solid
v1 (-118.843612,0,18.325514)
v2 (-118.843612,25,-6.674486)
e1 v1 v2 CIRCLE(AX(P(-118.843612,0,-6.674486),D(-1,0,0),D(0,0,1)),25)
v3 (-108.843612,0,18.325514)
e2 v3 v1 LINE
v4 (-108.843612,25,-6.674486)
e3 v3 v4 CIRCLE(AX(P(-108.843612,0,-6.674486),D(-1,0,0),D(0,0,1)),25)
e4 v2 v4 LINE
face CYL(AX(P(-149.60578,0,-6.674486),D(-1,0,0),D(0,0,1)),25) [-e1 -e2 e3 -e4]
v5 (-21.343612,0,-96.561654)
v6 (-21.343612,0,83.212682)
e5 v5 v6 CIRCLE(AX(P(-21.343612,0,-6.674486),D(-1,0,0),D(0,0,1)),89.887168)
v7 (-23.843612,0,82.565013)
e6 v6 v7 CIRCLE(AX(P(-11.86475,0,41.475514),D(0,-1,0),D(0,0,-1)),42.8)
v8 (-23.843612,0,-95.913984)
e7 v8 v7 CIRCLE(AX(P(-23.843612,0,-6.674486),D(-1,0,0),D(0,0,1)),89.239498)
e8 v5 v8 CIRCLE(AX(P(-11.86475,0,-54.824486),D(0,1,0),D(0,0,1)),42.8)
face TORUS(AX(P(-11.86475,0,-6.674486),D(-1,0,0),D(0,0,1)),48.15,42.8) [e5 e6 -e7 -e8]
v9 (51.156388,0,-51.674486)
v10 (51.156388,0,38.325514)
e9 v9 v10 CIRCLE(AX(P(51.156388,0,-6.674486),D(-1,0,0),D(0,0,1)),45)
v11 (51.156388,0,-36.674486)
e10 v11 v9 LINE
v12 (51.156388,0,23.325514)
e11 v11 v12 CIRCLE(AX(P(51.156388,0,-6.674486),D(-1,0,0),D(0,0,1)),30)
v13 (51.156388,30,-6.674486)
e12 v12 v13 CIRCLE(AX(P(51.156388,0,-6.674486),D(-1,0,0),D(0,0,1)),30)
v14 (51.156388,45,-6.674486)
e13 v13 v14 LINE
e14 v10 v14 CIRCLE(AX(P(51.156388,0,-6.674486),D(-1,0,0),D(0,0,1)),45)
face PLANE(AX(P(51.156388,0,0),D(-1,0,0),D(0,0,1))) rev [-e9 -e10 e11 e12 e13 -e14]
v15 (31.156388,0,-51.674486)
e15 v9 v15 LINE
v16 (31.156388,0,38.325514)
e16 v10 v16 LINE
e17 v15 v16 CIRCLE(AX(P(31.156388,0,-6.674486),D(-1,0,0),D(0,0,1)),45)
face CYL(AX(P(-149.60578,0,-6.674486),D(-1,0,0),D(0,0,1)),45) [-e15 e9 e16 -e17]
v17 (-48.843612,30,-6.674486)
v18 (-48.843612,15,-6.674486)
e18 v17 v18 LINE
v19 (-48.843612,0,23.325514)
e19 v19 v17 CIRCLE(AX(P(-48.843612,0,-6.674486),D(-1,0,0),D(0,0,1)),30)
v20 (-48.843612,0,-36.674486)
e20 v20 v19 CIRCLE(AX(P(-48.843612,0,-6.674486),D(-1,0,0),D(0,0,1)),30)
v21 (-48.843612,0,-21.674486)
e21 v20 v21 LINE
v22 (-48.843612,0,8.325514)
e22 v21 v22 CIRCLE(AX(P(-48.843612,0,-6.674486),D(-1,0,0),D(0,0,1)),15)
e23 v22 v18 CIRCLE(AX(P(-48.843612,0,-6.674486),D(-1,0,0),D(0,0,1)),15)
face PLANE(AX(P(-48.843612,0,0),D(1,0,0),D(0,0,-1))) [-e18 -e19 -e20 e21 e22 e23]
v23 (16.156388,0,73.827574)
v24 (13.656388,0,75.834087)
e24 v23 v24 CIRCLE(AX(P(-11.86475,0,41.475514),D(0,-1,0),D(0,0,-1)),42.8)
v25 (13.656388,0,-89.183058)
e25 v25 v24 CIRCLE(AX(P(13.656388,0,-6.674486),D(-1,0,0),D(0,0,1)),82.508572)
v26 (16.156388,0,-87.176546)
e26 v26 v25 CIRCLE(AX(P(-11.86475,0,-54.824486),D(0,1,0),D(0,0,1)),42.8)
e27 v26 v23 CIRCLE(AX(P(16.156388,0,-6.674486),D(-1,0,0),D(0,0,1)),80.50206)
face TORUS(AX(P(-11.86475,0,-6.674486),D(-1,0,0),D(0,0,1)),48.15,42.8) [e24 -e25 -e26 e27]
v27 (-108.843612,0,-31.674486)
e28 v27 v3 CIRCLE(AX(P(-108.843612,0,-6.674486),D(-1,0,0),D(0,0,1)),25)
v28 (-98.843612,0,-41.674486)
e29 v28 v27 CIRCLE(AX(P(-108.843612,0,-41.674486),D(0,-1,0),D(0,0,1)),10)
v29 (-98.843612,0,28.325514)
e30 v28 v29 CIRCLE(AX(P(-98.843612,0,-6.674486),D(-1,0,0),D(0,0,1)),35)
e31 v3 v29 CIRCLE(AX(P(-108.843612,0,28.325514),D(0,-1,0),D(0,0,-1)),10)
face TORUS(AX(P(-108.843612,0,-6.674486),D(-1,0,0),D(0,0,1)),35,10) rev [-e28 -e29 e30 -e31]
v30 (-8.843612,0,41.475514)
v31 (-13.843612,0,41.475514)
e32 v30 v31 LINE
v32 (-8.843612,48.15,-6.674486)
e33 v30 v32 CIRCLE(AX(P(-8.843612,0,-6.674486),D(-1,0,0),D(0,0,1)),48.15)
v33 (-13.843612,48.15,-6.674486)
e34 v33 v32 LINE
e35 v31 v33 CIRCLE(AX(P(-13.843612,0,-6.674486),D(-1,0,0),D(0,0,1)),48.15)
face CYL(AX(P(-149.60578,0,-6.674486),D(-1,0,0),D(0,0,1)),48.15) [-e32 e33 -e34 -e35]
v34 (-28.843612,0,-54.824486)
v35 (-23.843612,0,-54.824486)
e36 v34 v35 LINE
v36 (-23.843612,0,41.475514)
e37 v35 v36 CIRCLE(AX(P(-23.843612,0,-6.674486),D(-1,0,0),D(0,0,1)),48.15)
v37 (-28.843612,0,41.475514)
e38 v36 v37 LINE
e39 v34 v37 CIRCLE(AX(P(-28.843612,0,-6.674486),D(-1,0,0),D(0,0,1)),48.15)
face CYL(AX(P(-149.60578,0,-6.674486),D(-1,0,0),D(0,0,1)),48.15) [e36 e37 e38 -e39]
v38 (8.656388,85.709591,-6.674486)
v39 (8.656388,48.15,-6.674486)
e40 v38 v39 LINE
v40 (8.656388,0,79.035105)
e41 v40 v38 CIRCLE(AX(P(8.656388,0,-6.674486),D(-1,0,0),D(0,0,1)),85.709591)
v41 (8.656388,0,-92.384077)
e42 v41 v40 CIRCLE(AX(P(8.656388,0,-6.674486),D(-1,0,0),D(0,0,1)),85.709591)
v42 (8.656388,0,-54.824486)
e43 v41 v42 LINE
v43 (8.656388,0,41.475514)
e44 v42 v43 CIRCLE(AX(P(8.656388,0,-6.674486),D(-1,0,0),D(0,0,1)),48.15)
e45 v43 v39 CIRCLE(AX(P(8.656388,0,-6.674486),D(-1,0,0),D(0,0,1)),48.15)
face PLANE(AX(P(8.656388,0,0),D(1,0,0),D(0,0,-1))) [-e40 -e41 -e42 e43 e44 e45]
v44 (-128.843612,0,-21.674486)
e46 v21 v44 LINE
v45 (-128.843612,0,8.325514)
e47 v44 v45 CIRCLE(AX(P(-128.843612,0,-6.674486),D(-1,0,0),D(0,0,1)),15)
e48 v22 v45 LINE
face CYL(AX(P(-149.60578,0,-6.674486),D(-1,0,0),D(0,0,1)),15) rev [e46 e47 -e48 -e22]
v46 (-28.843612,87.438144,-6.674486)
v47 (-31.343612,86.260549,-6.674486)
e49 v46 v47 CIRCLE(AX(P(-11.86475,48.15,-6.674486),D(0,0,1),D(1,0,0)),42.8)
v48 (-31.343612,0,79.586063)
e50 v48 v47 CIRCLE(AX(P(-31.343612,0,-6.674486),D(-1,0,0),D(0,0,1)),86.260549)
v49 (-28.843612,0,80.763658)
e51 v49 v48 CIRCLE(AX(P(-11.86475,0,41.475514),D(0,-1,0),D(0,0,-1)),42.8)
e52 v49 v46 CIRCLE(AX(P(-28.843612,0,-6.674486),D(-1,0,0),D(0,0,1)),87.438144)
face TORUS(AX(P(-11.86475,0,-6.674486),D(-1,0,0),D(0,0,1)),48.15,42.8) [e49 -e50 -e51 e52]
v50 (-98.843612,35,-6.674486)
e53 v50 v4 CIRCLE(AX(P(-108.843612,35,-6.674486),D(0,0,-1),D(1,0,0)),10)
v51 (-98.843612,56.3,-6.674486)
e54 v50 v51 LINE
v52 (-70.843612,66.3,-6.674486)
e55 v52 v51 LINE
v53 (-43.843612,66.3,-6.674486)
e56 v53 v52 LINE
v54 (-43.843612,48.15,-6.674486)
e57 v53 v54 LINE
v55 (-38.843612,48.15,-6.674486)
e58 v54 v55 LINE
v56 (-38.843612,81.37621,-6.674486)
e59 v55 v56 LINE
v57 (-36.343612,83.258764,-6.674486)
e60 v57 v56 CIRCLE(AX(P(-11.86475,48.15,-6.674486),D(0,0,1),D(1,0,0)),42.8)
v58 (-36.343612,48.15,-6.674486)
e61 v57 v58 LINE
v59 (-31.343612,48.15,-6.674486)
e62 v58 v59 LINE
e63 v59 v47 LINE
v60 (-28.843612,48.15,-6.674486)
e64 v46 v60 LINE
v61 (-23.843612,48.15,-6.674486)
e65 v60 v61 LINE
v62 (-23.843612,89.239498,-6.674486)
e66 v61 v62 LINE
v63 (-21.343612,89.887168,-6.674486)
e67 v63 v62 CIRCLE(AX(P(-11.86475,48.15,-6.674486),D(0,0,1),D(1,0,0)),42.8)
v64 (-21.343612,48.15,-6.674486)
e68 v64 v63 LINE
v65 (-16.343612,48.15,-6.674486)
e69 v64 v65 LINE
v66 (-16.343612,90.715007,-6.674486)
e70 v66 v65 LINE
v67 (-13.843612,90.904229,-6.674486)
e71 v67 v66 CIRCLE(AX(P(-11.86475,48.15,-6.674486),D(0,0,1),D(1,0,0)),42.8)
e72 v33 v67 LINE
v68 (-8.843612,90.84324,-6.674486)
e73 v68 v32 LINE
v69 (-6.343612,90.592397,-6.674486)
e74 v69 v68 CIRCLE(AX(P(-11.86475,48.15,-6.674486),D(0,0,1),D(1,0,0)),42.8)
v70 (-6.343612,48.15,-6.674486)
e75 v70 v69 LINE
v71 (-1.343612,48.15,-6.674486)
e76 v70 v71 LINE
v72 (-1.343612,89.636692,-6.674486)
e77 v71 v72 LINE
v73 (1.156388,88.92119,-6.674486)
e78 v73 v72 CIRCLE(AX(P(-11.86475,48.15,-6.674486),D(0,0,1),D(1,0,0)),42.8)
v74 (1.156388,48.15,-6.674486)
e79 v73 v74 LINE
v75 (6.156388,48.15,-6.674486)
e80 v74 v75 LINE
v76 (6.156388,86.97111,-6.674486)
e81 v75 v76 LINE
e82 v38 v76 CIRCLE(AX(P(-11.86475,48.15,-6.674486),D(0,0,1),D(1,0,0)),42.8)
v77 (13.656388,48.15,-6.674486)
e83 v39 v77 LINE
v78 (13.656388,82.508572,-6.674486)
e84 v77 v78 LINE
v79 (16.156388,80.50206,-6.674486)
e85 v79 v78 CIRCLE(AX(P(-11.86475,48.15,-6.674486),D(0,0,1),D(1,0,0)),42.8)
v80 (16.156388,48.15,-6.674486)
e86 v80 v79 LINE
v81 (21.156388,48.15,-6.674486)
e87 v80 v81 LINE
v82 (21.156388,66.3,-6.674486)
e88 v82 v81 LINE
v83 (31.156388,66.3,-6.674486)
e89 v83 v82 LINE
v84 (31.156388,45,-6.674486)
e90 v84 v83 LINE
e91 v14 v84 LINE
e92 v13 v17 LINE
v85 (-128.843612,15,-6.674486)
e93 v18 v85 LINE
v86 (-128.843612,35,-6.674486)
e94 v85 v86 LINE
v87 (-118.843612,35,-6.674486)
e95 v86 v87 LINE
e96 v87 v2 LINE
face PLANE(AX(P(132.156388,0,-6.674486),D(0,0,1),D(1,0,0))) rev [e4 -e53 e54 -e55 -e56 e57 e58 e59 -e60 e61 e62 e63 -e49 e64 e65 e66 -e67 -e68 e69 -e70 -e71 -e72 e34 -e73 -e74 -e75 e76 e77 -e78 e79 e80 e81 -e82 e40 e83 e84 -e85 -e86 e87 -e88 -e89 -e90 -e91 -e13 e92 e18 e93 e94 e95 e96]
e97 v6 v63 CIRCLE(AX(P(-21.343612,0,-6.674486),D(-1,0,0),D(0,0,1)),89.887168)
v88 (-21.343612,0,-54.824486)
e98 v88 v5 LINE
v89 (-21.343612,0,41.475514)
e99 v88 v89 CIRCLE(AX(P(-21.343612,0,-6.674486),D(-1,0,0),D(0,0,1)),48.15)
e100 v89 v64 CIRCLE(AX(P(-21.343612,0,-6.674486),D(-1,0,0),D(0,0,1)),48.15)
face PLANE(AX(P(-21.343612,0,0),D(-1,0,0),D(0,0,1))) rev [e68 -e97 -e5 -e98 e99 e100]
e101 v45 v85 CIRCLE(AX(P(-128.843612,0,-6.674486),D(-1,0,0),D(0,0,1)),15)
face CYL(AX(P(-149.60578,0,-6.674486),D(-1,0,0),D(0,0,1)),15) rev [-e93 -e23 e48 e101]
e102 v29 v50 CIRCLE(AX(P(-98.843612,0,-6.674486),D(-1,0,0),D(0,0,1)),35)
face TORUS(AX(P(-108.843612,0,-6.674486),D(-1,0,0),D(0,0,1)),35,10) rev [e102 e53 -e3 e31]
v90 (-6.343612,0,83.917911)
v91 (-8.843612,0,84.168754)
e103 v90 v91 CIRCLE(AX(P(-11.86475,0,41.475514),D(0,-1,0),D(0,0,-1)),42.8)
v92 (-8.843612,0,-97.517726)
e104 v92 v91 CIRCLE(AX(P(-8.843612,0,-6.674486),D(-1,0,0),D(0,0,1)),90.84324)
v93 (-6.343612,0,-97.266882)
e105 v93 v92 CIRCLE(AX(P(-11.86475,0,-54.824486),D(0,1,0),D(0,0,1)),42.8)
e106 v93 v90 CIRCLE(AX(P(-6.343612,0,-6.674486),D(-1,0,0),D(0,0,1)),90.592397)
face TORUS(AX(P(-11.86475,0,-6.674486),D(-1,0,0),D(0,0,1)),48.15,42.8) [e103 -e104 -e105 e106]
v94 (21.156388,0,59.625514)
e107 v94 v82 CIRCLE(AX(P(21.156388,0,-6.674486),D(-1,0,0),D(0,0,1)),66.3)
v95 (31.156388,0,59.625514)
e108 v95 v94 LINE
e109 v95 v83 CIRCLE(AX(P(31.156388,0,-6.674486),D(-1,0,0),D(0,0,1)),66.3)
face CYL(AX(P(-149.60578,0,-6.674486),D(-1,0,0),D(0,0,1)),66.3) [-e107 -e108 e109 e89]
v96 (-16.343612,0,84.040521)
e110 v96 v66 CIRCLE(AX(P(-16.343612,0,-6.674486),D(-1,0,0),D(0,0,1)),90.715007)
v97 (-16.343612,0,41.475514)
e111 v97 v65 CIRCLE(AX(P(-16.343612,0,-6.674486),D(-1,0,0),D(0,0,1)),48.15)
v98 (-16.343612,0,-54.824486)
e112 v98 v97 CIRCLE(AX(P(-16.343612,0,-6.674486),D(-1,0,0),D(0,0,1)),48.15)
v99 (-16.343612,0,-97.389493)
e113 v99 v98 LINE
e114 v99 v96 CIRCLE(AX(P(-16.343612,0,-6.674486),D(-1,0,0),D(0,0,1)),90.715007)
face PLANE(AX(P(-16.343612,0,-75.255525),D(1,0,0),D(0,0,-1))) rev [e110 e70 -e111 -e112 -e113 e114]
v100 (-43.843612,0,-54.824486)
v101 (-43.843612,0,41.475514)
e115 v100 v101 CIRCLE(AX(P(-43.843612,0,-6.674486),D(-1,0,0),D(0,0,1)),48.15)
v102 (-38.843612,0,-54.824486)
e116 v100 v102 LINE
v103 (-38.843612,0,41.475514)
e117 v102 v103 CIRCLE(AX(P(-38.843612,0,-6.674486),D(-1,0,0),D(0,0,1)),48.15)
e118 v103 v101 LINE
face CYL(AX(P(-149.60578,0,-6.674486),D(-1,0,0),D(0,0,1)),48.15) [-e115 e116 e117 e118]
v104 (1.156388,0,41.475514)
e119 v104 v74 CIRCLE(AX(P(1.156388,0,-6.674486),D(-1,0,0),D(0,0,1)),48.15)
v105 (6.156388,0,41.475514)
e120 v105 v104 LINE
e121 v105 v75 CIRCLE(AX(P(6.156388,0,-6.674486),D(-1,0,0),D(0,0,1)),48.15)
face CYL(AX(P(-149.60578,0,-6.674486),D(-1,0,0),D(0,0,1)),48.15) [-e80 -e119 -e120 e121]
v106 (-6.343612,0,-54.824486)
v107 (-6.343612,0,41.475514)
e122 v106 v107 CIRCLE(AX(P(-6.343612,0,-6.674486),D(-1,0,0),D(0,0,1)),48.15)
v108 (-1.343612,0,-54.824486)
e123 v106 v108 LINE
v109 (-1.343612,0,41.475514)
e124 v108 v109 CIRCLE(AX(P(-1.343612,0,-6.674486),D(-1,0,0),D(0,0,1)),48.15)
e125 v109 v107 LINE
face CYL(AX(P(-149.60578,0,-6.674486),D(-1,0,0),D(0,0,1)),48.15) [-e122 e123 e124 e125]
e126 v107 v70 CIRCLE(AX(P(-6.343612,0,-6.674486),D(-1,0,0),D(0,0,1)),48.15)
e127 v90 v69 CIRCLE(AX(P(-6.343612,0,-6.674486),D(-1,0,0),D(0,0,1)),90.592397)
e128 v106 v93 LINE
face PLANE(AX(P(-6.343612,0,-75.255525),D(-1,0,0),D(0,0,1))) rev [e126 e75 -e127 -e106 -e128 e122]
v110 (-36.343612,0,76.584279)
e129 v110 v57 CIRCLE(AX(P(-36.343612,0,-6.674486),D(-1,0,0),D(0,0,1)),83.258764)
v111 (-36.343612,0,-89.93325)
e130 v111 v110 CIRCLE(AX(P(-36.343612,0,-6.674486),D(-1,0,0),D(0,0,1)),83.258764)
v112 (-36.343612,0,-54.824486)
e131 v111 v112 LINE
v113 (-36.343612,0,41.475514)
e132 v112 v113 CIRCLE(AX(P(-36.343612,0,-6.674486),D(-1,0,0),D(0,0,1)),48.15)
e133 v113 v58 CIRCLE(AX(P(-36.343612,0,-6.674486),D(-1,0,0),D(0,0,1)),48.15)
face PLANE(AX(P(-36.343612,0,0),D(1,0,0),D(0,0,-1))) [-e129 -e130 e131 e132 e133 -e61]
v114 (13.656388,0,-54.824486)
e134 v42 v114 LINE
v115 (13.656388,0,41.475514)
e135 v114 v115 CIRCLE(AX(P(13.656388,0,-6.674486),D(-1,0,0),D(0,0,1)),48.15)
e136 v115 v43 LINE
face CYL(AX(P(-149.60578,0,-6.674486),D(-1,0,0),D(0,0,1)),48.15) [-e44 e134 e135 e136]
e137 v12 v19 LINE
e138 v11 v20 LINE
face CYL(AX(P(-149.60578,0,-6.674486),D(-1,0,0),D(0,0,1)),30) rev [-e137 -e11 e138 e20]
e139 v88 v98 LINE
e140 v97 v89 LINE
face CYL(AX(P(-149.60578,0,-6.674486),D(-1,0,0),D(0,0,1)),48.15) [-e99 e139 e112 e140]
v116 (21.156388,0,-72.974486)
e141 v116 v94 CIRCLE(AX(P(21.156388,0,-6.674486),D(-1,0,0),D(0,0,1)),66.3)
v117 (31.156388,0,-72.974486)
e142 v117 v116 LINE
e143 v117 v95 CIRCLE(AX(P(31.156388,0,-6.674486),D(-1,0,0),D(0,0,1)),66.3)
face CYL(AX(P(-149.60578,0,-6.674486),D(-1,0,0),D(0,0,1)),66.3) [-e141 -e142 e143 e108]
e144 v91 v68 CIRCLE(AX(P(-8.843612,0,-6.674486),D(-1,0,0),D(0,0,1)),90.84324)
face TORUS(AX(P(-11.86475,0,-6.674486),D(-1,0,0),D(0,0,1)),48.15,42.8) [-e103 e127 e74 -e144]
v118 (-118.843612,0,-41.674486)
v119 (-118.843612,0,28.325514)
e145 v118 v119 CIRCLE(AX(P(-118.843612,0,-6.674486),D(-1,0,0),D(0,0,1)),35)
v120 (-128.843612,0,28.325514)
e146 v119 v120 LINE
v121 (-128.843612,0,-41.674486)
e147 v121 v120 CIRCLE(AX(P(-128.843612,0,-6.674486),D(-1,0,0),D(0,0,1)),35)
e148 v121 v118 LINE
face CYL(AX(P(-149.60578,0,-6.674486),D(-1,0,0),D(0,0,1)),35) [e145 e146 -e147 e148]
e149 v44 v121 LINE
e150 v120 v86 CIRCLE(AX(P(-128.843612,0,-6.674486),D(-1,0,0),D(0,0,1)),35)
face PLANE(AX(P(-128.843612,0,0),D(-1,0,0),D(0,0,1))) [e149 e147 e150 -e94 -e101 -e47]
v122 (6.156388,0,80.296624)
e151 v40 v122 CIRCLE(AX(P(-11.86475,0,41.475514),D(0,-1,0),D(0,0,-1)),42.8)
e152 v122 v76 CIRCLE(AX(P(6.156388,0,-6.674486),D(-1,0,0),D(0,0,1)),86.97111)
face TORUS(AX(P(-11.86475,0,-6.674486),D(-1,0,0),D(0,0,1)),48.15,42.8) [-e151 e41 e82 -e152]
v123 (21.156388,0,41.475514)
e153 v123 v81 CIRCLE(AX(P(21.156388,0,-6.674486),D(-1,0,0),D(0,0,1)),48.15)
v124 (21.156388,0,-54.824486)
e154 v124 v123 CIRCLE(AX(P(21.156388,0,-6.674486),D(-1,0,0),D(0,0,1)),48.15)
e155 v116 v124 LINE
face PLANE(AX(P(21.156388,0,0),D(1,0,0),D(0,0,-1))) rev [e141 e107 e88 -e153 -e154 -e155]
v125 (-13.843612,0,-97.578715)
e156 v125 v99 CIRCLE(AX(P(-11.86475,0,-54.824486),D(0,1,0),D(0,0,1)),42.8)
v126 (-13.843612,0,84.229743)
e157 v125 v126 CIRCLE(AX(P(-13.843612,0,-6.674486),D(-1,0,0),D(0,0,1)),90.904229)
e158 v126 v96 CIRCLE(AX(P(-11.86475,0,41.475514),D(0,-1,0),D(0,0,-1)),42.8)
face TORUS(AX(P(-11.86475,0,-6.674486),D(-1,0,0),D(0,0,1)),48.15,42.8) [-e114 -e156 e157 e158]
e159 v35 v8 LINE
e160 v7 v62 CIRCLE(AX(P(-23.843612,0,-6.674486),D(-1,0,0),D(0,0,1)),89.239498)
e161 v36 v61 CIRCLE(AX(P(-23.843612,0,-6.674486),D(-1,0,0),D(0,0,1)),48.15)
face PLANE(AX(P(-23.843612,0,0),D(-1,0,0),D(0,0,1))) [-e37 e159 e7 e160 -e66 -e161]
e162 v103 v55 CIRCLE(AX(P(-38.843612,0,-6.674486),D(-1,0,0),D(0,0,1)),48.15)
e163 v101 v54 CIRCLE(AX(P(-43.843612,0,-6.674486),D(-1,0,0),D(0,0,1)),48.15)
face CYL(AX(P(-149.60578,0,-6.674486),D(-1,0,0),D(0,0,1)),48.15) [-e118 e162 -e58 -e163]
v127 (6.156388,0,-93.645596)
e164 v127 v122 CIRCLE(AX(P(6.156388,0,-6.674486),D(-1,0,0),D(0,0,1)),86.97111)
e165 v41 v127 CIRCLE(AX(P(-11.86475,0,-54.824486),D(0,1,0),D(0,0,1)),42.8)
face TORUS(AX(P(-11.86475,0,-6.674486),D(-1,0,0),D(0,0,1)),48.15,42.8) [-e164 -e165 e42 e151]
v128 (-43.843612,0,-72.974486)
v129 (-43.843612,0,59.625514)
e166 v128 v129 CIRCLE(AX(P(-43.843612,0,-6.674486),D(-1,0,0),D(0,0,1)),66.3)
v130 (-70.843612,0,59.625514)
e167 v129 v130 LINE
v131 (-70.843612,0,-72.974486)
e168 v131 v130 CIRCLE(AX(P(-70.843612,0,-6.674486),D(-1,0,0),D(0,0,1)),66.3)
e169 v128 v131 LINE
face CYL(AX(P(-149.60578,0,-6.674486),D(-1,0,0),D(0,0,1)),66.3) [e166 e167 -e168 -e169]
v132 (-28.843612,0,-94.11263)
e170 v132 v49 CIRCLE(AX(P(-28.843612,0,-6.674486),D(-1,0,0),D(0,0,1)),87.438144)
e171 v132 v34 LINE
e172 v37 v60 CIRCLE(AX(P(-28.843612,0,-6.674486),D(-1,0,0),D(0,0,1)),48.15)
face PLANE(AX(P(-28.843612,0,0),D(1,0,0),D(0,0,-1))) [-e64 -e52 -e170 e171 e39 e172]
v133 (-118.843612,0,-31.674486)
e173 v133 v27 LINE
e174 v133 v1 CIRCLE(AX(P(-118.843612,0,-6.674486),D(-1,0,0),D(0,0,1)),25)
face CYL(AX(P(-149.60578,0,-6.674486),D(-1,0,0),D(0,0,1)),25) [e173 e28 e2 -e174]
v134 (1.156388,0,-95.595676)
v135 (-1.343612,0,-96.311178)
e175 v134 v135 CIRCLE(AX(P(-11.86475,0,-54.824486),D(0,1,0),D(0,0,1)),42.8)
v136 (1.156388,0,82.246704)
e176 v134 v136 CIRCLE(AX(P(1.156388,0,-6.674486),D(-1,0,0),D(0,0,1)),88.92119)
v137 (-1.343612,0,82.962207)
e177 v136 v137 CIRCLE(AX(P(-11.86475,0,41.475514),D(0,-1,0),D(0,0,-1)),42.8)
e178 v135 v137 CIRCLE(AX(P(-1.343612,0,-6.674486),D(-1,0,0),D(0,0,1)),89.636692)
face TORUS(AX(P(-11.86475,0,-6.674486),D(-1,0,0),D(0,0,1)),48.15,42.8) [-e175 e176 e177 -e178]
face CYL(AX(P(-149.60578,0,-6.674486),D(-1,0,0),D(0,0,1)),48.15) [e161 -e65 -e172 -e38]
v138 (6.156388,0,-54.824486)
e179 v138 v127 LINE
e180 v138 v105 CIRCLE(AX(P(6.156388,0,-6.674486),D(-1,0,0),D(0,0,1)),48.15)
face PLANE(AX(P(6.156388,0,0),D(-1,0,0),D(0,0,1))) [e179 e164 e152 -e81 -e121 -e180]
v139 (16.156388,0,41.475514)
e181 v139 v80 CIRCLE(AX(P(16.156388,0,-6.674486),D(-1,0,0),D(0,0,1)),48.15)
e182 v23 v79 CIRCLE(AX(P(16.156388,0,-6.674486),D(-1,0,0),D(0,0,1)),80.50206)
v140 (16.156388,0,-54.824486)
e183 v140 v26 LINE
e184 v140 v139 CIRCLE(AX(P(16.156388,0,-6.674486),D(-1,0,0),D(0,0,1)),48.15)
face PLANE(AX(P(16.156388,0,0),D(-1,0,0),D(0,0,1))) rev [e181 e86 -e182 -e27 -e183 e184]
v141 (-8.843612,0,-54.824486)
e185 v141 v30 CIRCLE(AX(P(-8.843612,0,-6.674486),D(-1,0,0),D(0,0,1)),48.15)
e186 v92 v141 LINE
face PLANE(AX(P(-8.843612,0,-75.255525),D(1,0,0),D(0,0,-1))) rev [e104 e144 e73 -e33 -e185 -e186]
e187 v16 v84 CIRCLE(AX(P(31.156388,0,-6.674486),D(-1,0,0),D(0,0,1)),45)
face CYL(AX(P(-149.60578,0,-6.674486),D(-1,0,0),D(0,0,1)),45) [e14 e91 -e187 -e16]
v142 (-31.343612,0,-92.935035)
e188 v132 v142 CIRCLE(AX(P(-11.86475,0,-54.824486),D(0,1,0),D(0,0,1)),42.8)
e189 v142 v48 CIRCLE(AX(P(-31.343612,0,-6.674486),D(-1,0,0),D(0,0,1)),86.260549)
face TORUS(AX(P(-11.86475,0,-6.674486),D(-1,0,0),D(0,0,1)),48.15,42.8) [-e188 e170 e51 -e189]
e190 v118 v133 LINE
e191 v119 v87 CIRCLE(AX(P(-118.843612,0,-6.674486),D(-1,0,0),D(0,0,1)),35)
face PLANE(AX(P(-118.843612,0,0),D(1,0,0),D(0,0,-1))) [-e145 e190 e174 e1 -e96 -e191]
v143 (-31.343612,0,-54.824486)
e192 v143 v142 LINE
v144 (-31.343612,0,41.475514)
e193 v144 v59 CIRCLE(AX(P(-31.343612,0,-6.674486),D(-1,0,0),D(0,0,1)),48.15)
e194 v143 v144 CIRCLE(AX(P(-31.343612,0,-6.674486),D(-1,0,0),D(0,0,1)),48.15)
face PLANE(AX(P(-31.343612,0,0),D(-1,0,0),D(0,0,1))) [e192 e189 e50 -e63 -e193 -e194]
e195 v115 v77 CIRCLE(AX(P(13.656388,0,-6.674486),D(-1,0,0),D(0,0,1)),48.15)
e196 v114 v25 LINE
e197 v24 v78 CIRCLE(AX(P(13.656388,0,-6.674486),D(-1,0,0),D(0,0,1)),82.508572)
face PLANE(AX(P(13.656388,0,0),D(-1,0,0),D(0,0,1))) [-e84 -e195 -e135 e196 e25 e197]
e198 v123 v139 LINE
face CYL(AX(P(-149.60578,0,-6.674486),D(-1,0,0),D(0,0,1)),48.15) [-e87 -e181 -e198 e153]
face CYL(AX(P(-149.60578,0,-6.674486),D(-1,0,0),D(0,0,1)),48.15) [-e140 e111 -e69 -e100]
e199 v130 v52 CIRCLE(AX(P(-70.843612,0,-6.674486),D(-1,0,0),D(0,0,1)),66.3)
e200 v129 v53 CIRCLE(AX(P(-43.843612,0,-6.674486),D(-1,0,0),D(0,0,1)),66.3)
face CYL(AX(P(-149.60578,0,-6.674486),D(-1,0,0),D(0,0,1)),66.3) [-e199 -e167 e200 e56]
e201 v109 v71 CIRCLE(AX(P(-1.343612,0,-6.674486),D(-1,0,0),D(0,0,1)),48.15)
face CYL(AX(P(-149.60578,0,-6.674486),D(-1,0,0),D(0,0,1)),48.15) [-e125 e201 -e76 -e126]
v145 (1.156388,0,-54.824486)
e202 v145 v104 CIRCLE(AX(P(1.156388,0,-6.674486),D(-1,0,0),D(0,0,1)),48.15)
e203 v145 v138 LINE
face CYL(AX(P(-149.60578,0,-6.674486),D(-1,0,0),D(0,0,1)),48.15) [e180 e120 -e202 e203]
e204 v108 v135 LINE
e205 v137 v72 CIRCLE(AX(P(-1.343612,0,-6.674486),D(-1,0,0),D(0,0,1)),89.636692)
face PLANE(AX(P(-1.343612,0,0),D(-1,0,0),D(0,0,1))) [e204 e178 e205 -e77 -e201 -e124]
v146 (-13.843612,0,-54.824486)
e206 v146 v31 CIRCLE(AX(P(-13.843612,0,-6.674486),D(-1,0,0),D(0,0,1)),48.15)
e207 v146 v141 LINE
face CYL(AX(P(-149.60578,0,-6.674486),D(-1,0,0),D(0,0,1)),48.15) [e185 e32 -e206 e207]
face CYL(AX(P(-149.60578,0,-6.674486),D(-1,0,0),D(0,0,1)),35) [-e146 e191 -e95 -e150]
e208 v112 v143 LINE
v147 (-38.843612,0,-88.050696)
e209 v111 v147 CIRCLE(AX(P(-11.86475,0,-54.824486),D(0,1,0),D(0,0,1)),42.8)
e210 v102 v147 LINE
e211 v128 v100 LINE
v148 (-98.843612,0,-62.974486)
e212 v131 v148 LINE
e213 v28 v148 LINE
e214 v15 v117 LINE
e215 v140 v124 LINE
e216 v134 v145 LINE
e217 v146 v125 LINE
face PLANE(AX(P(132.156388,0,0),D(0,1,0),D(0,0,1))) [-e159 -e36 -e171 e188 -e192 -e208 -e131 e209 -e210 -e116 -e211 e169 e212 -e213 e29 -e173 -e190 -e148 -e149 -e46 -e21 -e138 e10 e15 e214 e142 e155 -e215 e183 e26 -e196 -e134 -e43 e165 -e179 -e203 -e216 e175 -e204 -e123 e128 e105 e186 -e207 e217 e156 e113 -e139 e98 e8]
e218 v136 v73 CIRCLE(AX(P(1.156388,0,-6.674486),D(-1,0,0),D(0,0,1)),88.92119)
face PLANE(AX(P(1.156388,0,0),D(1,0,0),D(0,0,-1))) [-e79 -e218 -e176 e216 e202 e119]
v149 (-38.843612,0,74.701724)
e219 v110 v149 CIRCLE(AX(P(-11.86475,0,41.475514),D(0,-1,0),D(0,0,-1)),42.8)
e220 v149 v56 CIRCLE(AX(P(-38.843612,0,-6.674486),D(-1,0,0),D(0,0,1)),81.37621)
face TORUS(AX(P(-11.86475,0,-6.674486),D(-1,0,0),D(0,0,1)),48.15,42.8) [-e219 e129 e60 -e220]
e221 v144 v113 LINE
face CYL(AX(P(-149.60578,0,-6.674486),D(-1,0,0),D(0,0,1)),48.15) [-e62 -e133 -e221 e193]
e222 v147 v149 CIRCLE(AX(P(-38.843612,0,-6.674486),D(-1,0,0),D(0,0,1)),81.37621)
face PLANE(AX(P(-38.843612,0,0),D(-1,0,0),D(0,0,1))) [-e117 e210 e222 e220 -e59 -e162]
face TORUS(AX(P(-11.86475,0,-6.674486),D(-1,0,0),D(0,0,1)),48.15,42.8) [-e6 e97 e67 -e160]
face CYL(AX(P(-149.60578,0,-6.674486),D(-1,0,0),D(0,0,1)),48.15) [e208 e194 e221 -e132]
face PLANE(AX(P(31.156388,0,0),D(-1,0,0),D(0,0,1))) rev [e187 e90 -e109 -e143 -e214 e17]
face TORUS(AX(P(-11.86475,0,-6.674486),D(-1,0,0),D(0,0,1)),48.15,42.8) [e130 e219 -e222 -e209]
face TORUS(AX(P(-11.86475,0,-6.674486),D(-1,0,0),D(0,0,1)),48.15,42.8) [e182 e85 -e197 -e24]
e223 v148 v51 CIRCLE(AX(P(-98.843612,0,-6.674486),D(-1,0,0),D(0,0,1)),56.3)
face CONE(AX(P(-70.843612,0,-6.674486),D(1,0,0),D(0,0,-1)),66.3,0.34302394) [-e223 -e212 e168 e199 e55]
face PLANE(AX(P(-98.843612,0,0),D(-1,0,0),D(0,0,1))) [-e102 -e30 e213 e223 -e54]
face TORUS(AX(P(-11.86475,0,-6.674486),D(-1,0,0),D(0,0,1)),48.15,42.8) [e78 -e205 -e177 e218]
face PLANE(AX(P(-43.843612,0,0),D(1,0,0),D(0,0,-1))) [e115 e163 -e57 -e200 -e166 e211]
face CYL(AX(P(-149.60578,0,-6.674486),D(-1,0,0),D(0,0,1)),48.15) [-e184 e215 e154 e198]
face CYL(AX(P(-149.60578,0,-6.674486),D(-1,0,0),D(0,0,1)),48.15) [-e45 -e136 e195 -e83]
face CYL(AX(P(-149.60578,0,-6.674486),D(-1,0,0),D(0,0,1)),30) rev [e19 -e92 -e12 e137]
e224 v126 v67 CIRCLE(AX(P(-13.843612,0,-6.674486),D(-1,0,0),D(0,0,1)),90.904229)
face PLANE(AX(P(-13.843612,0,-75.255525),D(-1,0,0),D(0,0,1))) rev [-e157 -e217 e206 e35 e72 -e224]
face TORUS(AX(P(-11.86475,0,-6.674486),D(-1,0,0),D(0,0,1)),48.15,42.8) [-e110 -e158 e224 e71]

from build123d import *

# Parameters (mm, degrees)
SLOT_CUT_DEPTH      = 81
SLOT_CUT_DEPTH_BACK = 267
SLOT_CUT_SKETCH_W   = 99.104546372
SLOT_CUT_SKETCH_H   = 99.716302831


with BuildPart() as part:
    # Shaft Profile Sketch → Revolved Shaft Body (revolve)
    with BuildSketch(Plane(origin=(0, 0, 0), x_dir=(1, 0, 0), z_dir=(0, 1, 0)), mode=Mode.PRIVATE) as revolved_shaft_body_sk:
        with BuildLine():
            Line((51.156388298, 36.67448577), (51.156388298, 51.67448577))
            Line((51.156388298, 51.67448577), (31.156388298, 51.67448577))
            Line((31.156388298, 51.67448577), (31.156388298, 72.97448577))
            Line((31.156388298, 72.97448577), (21.156388298, 72.97448577))
            Line((21.156388298, 72.97448577), (21.156388298, 54.82448577))
            Line((21.156388298, 54.82448577), (16.156388298, 54.82448577))
            Line((16.156388298, 54.82448577), (16.156388298, 75.255525061))
            Line((16.156388298, 75.255525061), (16.156388298, 87.176546037))
            ThreePointArc((16.156388298, 87.176546037), (14.925180355, 88.203215925), (13.656388298, 89.183058142))
            Line((13.656388298, 89.183058142), (13.656388298, 75.255525061))
            Line((13.656388298, 75.255525061), (13.656388298, 54.82448577))
            Line((13.656388298, 54.82448577), (8.656388298, 54.82448577))
            Line((8.656388298, 54.82448577), (8.656388298, 75.255525061))
            Line((8.656388298, 75.255525061), (8.656388298, 92.384076813))
            ThreePointArc((8.656388298, 92.384076813), (7.416708158, 93.035287487), (6.156388298, 93.645595636))
            Line((6.156388298, 93.645595636), (6.156388298, 75.255525061))
            Line((6.156388298, 75.255525061), (6.156388298, 54.82448577))
            Line((6.156388298, 54.82448577), (1.156388298, 54.82448577))
            Line((1.156388298, 54.82448577), (1.156388298, 75.255525061))
            Line((1.156388298, 75.255525061), (1.156388298, 95.595676029))
            ThreePointArc((1.156388298, 95.595676029), (-0.088176532, 95.972417859), (-1.343611702, 96.311178179))
            Line((-1.343611702, 96.311178179), (-1.343611702, 75.255525061))
            Line((-1.343611702, 75.255525061), (-1.343611702, 54.82448577))
            Line((-1.343611702, 54.82448577), (-6.343611702, 54.82448577))
            Line((-6.343611702, 54.82448577), (-6.343611702, 75.255525061))
            Line((-6.343611702, 75.255525061), (-6.343611702, 97.266882391))
            ThreePointArc((-6.343611702, 97.266882391), (-7.591770603, 97.410653082), (-8.843611702, 97.517725549))
            Line((-8.843611702, 97.517725549), (-8.843611702, 92.720576379))
            Line((-8.843611702, 92.720576379), (-8.843611702, 75.255525061))
            Line((-8.843611702, 75.255525061), (-8.843611702, 54.82448577))
            Line((-8.843611702, 54.82448577), (-13.843611702, 54.82448577))
            Line((-13.843611702, 54.82448577), (-13.843611702, 75.255525061))
            Line((-13.843611702, 75.255525061), (-13.843611702, 97.578714879))
            ThreePointArc((-13.843611702, 97.578714879), (-15.09499754, 97.502413337), (-16.343611702, 97.389492508))
            Line((-16.343611702, 97.389492508), (-16.343611702, 75.255525061))
            Line((-16.343611702, 75.255525061), (-16.343611702, 54.82448577))
            Line((-16.343611702, 54.82448577), (-21.343611702, 54.82448577))
            Line((-21.343611702, 54.82448577), (-21.343611702, 75.255525061))
            Line((-21.343611702, 75.255525061), (-21.343611702, 96.561653648))
            ThreePointArc((-21.343611702, 96.561653648), (-22.598497826, 96.256679286), (-23.843611702, 95.913984117))
            Line((-23.843611702, 95.913984117), (-23.843611702, 75.255525061))
            Line((-23.843611702, 75.255525061), (-23.843611702, 54.82448577))
            Line((-23.843611702, 54.82448577), (-28.843611702, 54.82448577))
            Line((-28.843611702, 54.82448577), (-28.843611702, 75.255525061))
            Line((-28.843611702, 75.255525061), (-28.843611702, 94.112629762))
            ThreePointArc((-28.843611702, 94.112629762), (-30.103118387, 93.544014716), (-31.343611702, 92.935034838))
            Line((-31.343611702, 92.935034838), (-31.343611702, 75.255525061))
            Line((-31.343611702, 75.255525061), (-31.343611702, 54.82448577))
            Line((-31.343611702, 54.82448577), (-36.343611702, 54.82448577))
            Line((-36.343611702, 54.82448577), (-36.343611702, 75.255525061))
            Line((-36.343611702, 75.255525061), (-36.343611702, 89.933250119))
            ThreePointArc((-36.343611702, 89.933250119), (-37.610824017, 89.014830566), (-38.843611702, 88.050695696))
            Line((-38.843611702, 88.050695696), (-38.843611702, 75.255525061))
            Line((-38.843611702, 75.255525061), (-38.843611702, 54.82448577))
            Line((-38.843611702, 54.82448577), (-43.843611702, 54.82448577))
            Line((-43.843611702, 54.82448577), (-43.843611702, 72.97448577))
            Line((-43.843611702, 72.97448577), (-70.843611702, 72.97448577))
            Line((-70.843611702, 72.97448577), (-98.843611702, 62.97448577))
            Line((-98.843611702, 62.97448577), (-98.843611702, 41.67448577))
            ThreePointArc((-98.843611702, 41.67448577), (-101.772543891, 34.603417958), (-108.843611702, 31.67448577))
            Line((-108.843611702, 31.67448577), (-118.843611702, 31.67448577))
            Line((-118.843611702, 31.67448577), (-118.843611702, 41.67448577))
            Line((-118.843611702, 41.67448577), (-128.843611702, 41.67448577))
            Line((-128.843611702, 41.67448577), (-128.843611702, 21.67448577))
            Line((-128.843611702, 21.67448577), (-48.843611702, 21.67448577))
            Line((-48.843611702, 21.67448577), (-48.843611702, 36.67448577))
            Line((-48.843611702, 36.67448577), (51.156388298, 36.67448577))
        make_face()
    revolve(revolved_shaft_body_sk.sketch.rotate(Axis((-149.605779726, 0, -6.67448577), (1, 0, 0)), 180), axis=Axis((-149.605779726, 0, -6.67448577), (1, 0, 0)))

    # Slot Cut Sketch → Slot Cut (cut, two sides: drawn at the far end of the back side and taken through both)
    with BuildSketch(Plane(origin=(51.156388298, 0, 0), x_dir=(0, 0, -1), z_dir=(1, 0, 0)).offset(-SLOT_CUT_DEPTH_BACK)):
        with Locations((56.226758956, 49.858151416)):
            Rectangle(SLOT_CUT_SKETCH_W, SLOT_CUT_SKETCH_H)
    extrude(amount=SLOT_CUT_DEPTH + SLOT_CUT_DEPTH_BACK, mode=Mode.SUBTRACT)


solid = part.part
